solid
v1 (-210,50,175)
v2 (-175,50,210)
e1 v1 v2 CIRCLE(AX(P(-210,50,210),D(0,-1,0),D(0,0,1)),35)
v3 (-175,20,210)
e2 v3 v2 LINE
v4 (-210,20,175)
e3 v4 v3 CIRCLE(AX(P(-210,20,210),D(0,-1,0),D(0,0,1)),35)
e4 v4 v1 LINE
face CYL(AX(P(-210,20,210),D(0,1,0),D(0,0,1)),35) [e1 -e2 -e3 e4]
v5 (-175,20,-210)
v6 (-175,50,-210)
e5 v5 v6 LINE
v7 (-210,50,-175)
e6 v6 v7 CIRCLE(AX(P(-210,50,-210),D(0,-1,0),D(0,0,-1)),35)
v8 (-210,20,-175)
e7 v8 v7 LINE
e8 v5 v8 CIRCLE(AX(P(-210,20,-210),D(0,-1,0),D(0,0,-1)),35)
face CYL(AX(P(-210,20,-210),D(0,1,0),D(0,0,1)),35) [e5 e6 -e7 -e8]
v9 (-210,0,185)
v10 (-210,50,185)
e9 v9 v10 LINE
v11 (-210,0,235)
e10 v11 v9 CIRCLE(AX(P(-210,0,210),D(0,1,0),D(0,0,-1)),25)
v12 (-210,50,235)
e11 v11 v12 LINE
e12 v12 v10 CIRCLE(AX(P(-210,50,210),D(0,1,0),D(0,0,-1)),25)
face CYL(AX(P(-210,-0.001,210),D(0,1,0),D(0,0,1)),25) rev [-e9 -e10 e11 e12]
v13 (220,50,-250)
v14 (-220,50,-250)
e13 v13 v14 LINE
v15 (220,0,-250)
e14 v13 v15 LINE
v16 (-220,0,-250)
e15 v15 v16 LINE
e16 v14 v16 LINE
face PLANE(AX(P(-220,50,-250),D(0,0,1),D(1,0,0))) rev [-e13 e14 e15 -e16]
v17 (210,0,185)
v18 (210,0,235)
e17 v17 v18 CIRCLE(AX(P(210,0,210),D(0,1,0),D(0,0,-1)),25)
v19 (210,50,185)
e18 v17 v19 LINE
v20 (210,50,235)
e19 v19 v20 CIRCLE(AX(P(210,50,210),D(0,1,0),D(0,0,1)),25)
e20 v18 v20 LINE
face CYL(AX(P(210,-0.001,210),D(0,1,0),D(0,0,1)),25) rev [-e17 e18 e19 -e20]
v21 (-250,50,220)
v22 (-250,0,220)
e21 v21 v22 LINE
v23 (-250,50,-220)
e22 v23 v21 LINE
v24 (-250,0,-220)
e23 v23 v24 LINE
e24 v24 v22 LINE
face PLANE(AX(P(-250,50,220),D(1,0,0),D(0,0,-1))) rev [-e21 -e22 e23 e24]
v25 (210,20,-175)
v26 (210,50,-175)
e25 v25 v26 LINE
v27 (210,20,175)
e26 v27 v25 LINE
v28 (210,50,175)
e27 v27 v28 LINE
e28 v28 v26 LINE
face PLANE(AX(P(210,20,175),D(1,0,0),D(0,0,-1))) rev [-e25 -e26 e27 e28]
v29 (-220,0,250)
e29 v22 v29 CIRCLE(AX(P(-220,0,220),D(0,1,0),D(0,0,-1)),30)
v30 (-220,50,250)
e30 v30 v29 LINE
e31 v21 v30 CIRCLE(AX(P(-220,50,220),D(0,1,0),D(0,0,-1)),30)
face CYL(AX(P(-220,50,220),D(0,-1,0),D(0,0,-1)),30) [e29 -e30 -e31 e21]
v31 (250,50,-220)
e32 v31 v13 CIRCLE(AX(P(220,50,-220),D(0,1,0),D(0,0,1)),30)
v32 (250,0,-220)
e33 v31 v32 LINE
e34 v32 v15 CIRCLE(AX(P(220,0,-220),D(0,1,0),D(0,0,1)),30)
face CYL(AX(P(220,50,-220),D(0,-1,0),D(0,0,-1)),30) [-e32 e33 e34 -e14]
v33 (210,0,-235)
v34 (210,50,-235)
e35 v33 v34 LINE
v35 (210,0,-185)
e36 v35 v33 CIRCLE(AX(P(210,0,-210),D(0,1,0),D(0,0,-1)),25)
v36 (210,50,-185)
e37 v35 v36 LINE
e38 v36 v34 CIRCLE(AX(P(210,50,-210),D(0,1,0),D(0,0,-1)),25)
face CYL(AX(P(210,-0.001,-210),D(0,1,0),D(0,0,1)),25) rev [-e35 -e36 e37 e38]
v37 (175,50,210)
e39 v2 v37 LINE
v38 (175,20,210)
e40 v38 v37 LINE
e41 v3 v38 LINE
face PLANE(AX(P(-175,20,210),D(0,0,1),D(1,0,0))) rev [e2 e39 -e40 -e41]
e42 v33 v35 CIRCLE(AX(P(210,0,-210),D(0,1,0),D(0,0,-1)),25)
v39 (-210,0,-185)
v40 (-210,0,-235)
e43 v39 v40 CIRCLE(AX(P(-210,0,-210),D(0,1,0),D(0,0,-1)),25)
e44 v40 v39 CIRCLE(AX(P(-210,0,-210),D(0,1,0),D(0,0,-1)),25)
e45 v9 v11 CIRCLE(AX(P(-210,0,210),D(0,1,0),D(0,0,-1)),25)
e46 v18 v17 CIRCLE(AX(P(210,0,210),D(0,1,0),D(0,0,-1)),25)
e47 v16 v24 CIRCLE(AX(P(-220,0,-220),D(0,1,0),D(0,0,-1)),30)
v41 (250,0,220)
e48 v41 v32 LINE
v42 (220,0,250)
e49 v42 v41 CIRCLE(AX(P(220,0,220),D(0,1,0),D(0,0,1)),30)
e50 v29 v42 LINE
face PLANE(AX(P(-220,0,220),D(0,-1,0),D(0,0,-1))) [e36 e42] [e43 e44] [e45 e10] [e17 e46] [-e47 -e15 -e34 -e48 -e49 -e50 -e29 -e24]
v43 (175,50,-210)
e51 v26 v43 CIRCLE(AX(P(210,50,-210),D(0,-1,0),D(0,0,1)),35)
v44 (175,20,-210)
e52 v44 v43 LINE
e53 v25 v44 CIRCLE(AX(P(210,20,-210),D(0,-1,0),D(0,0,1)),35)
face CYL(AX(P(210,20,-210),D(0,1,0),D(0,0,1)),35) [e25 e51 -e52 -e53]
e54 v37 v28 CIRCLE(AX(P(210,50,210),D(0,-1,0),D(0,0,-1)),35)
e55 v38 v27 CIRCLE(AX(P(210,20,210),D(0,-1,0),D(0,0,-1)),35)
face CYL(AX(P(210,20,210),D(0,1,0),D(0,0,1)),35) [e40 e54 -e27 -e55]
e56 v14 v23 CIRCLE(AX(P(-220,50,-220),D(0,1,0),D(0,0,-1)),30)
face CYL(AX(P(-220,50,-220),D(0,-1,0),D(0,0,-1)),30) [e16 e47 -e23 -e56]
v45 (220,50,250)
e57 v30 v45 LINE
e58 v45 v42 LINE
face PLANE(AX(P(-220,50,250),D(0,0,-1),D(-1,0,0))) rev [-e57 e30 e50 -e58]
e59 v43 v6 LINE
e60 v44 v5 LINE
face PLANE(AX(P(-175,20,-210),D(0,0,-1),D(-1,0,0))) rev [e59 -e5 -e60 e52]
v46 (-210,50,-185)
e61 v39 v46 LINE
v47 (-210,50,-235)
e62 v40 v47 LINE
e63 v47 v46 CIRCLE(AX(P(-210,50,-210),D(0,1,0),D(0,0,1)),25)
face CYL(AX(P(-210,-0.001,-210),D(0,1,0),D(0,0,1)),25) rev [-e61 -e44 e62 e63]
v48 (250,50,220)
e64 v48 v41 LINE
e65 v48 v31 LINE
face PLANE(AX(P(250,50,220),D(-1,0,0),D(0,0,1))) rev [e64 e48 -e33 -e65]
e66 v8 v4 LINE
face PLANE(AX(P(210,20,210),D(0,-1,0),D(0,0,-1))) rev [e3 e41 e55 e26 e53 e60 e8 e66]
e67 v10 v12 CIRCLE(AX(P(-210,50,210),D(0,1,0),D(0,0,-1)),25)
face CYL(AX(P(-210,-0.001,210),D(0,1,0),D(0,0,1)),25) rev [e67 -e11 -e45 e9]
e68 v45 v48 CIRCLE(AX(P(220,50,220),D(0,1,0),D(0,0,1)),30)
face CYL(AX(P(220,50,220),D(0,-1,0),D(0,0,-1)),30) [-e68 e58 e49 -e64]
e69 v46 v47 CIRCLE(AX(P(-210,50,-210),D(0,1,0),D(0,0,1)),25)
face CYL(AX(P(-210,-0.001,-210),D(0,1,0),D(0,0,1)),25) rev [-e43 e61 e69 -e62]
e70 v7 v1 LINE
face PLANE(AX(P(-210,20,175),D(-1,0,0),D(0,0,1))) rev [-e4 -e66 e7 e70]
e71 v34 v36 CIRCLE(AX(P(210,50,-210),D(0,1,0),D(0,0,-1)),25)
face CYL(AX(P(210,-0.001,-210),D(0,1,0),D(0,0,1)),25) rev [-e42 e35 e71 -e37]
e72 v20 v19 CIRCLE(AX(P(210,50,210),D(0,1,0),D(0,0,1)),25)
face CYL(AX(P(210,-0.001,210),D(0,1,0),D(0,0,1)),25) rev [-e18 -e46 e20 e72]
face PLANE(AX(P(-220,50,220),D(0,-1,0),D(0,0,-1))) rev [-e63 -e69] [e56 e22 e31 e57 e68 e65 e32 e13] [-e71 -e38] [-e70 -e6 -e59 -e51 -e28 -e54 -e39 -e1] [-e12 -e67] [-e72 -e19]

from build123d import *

# Parameters (mm, degrees)
BOSS_EXTRUDE1_DEPTH = 50
CUT_EXTRUDE1_DEPTH  = 30
CUT_EXTRUDE2_REACH  = 359.071
SKETCH3_R           = 25


with BuildPart() as part:
    # Sketch1 → Boss-Extrude1 (new body)
    with BuildSketch(Plane(origin=(0, 0, 0), x_dir=(1, 0, 0), z_dir=(0, 1, 0))):
        with BuildLine():
            Line((-220, -250), (220, -250))
            ThreePointArc((220, -250), (241.213203436, -241.213203436), (250, -220))
            Line((250, -220), (250, 220))
            ThreePointArc((250, 220), (241.213203436, 241.213203436), (220, 250))
            Line((220, 250), (-220, 250))
            ThreePointArc((-220, 250), (-241.213203436, 241.213203436), (-250, 220))
            Line((-250, 220), (-250, -220))
            ThreePointArc((-250, -220), (-241.213203436, -241.213203436), (-220, -250))
        make_face()
    extrude(amount=BOSS_EXTRUDE1_DEPTH)

    # Sketch2 → Cut-Extrude1 (cut)
    with BuildSketch(Plane(origin=(0, 50, 0), x_dir=(1, 0, 0), z_dir=(0, 1, 0))):
        with BuildLine():
            Line((-175, -210), (175, -210))
            ThreePointArc((175, -210), (185.251262658, -185.251262658), (210, -175))
            Line((210, -175), (210, 175))
            ThreePointArc((210, 175), (185.251262658, 185.251262658), (175, 210))
            Line((175, 210), (-175, 210))
            ThreePointArc((-175, 210), (-185.251262658, 185.251262658), (-210, 175))
            Line((-210, 175), (-210, -175))
            ThreePointArc((-210, -175), (-185.251262658, -185.251262658), (-175, -210))
        make_face()
    extrude(amount=-CUT_EXTRUDE1_DEPTH, mode=Mode.SUBTRACT)

    # Sketch3 → Cut-Extrude2 (cut, up to next)
    with BuildSketch(Plane(origin=(0, 50, 0), x_dir=(1, 0, 0), z_dir=(0, 1, 0)), mode=Mode.PRIVATE) as cut_extrude2_sk1:
        with Locations(Location((-210, 210, 0), (0, 0, 270))):
            Circle(SKETCH3_R)
    cut_extrude2_tool1 = extrude(cut_extrude2_sk1.sketch, amount=-CUT_EXTRUDE2_REACH, mode=Mode.PRIVATE) & part.part
    # Sketch3 → Cut-Extrude2 (cut, up to next)
    with BuildSketch(Plane(origin=(0, 50, 0), x_dir=(1, 0, 0), z_dir=(0, 1, 0)), mode=Mode.PRIVATE) as cut_extrude2_sk2:
        with Locations(Location((210, 210, 0), (0, 0, 90))):
            Circle(SKETCH3_R)
    cut_extrude2_tool2 = extrude(cut_extrude2_sk2.sketch, amount=-CUT_EXTRUDE2_REACH, mode=Mode.PRIVATE) & part.part
    # Sketch3 → Cut-Extrude2 (cut, up to next)
    with BuildSketch(Plane(origin=(0, 50, 0), x_dir=(1, 0, 0), z_dir=(0, 1, 0)), mode=Mode.PRIVATE) as cut_extrude2_sk3:
        with Locations(Location((210, -210, 0), (0, 0, 270))):
            Circle(SKETCH3_R)
    cut_extrude2_tool3 = extrude(cut_extrude2_sk3.sketch, amount=-CUT_EXTRUDE2_REACH, mode=Mode.PRIVATE) & part.part
    # Sketch3 → Cut-Extrude2 (cut, up to next)
    with BuildSketch(Plane(origin=(0, 50, 0), x_dir=(1, 0, 0), z_dir=(0, 1, 0)), mode=Mode.PRIVATE) as cut_extrude2_sk4:
        with Locations(Location((-210, -210, 0), (0, 0, 90))):
            Circle(SKETCH3_R)
    cut_extrude2_tool4 = extrude(cut_extrude2_sk4.sketch, amount=-CUT_EXTRUDE2_REACH, mode=Mode.PRIVATE) & part.part
    add(cut_extrude2_tool1.solids().sort_by_distance((-210, 50, -210))[0], mode=Mode.SUBTRACT)
    add(cut_extrude2_tool2.solids().sort_by_distance((210, 50, -210))[0], mode=Mode.SUBTRACT)
    add(cut_extrude2_tool3.solids().sort_by_distance((210, 50, 210))[0], mode=Mode.SUBTRACT)
    add(cut_extrude2_tool4.solids().sort_by_distance((-210, 50, 210))[0], mode=Mode.SUBTRACT)


solid = part.part
